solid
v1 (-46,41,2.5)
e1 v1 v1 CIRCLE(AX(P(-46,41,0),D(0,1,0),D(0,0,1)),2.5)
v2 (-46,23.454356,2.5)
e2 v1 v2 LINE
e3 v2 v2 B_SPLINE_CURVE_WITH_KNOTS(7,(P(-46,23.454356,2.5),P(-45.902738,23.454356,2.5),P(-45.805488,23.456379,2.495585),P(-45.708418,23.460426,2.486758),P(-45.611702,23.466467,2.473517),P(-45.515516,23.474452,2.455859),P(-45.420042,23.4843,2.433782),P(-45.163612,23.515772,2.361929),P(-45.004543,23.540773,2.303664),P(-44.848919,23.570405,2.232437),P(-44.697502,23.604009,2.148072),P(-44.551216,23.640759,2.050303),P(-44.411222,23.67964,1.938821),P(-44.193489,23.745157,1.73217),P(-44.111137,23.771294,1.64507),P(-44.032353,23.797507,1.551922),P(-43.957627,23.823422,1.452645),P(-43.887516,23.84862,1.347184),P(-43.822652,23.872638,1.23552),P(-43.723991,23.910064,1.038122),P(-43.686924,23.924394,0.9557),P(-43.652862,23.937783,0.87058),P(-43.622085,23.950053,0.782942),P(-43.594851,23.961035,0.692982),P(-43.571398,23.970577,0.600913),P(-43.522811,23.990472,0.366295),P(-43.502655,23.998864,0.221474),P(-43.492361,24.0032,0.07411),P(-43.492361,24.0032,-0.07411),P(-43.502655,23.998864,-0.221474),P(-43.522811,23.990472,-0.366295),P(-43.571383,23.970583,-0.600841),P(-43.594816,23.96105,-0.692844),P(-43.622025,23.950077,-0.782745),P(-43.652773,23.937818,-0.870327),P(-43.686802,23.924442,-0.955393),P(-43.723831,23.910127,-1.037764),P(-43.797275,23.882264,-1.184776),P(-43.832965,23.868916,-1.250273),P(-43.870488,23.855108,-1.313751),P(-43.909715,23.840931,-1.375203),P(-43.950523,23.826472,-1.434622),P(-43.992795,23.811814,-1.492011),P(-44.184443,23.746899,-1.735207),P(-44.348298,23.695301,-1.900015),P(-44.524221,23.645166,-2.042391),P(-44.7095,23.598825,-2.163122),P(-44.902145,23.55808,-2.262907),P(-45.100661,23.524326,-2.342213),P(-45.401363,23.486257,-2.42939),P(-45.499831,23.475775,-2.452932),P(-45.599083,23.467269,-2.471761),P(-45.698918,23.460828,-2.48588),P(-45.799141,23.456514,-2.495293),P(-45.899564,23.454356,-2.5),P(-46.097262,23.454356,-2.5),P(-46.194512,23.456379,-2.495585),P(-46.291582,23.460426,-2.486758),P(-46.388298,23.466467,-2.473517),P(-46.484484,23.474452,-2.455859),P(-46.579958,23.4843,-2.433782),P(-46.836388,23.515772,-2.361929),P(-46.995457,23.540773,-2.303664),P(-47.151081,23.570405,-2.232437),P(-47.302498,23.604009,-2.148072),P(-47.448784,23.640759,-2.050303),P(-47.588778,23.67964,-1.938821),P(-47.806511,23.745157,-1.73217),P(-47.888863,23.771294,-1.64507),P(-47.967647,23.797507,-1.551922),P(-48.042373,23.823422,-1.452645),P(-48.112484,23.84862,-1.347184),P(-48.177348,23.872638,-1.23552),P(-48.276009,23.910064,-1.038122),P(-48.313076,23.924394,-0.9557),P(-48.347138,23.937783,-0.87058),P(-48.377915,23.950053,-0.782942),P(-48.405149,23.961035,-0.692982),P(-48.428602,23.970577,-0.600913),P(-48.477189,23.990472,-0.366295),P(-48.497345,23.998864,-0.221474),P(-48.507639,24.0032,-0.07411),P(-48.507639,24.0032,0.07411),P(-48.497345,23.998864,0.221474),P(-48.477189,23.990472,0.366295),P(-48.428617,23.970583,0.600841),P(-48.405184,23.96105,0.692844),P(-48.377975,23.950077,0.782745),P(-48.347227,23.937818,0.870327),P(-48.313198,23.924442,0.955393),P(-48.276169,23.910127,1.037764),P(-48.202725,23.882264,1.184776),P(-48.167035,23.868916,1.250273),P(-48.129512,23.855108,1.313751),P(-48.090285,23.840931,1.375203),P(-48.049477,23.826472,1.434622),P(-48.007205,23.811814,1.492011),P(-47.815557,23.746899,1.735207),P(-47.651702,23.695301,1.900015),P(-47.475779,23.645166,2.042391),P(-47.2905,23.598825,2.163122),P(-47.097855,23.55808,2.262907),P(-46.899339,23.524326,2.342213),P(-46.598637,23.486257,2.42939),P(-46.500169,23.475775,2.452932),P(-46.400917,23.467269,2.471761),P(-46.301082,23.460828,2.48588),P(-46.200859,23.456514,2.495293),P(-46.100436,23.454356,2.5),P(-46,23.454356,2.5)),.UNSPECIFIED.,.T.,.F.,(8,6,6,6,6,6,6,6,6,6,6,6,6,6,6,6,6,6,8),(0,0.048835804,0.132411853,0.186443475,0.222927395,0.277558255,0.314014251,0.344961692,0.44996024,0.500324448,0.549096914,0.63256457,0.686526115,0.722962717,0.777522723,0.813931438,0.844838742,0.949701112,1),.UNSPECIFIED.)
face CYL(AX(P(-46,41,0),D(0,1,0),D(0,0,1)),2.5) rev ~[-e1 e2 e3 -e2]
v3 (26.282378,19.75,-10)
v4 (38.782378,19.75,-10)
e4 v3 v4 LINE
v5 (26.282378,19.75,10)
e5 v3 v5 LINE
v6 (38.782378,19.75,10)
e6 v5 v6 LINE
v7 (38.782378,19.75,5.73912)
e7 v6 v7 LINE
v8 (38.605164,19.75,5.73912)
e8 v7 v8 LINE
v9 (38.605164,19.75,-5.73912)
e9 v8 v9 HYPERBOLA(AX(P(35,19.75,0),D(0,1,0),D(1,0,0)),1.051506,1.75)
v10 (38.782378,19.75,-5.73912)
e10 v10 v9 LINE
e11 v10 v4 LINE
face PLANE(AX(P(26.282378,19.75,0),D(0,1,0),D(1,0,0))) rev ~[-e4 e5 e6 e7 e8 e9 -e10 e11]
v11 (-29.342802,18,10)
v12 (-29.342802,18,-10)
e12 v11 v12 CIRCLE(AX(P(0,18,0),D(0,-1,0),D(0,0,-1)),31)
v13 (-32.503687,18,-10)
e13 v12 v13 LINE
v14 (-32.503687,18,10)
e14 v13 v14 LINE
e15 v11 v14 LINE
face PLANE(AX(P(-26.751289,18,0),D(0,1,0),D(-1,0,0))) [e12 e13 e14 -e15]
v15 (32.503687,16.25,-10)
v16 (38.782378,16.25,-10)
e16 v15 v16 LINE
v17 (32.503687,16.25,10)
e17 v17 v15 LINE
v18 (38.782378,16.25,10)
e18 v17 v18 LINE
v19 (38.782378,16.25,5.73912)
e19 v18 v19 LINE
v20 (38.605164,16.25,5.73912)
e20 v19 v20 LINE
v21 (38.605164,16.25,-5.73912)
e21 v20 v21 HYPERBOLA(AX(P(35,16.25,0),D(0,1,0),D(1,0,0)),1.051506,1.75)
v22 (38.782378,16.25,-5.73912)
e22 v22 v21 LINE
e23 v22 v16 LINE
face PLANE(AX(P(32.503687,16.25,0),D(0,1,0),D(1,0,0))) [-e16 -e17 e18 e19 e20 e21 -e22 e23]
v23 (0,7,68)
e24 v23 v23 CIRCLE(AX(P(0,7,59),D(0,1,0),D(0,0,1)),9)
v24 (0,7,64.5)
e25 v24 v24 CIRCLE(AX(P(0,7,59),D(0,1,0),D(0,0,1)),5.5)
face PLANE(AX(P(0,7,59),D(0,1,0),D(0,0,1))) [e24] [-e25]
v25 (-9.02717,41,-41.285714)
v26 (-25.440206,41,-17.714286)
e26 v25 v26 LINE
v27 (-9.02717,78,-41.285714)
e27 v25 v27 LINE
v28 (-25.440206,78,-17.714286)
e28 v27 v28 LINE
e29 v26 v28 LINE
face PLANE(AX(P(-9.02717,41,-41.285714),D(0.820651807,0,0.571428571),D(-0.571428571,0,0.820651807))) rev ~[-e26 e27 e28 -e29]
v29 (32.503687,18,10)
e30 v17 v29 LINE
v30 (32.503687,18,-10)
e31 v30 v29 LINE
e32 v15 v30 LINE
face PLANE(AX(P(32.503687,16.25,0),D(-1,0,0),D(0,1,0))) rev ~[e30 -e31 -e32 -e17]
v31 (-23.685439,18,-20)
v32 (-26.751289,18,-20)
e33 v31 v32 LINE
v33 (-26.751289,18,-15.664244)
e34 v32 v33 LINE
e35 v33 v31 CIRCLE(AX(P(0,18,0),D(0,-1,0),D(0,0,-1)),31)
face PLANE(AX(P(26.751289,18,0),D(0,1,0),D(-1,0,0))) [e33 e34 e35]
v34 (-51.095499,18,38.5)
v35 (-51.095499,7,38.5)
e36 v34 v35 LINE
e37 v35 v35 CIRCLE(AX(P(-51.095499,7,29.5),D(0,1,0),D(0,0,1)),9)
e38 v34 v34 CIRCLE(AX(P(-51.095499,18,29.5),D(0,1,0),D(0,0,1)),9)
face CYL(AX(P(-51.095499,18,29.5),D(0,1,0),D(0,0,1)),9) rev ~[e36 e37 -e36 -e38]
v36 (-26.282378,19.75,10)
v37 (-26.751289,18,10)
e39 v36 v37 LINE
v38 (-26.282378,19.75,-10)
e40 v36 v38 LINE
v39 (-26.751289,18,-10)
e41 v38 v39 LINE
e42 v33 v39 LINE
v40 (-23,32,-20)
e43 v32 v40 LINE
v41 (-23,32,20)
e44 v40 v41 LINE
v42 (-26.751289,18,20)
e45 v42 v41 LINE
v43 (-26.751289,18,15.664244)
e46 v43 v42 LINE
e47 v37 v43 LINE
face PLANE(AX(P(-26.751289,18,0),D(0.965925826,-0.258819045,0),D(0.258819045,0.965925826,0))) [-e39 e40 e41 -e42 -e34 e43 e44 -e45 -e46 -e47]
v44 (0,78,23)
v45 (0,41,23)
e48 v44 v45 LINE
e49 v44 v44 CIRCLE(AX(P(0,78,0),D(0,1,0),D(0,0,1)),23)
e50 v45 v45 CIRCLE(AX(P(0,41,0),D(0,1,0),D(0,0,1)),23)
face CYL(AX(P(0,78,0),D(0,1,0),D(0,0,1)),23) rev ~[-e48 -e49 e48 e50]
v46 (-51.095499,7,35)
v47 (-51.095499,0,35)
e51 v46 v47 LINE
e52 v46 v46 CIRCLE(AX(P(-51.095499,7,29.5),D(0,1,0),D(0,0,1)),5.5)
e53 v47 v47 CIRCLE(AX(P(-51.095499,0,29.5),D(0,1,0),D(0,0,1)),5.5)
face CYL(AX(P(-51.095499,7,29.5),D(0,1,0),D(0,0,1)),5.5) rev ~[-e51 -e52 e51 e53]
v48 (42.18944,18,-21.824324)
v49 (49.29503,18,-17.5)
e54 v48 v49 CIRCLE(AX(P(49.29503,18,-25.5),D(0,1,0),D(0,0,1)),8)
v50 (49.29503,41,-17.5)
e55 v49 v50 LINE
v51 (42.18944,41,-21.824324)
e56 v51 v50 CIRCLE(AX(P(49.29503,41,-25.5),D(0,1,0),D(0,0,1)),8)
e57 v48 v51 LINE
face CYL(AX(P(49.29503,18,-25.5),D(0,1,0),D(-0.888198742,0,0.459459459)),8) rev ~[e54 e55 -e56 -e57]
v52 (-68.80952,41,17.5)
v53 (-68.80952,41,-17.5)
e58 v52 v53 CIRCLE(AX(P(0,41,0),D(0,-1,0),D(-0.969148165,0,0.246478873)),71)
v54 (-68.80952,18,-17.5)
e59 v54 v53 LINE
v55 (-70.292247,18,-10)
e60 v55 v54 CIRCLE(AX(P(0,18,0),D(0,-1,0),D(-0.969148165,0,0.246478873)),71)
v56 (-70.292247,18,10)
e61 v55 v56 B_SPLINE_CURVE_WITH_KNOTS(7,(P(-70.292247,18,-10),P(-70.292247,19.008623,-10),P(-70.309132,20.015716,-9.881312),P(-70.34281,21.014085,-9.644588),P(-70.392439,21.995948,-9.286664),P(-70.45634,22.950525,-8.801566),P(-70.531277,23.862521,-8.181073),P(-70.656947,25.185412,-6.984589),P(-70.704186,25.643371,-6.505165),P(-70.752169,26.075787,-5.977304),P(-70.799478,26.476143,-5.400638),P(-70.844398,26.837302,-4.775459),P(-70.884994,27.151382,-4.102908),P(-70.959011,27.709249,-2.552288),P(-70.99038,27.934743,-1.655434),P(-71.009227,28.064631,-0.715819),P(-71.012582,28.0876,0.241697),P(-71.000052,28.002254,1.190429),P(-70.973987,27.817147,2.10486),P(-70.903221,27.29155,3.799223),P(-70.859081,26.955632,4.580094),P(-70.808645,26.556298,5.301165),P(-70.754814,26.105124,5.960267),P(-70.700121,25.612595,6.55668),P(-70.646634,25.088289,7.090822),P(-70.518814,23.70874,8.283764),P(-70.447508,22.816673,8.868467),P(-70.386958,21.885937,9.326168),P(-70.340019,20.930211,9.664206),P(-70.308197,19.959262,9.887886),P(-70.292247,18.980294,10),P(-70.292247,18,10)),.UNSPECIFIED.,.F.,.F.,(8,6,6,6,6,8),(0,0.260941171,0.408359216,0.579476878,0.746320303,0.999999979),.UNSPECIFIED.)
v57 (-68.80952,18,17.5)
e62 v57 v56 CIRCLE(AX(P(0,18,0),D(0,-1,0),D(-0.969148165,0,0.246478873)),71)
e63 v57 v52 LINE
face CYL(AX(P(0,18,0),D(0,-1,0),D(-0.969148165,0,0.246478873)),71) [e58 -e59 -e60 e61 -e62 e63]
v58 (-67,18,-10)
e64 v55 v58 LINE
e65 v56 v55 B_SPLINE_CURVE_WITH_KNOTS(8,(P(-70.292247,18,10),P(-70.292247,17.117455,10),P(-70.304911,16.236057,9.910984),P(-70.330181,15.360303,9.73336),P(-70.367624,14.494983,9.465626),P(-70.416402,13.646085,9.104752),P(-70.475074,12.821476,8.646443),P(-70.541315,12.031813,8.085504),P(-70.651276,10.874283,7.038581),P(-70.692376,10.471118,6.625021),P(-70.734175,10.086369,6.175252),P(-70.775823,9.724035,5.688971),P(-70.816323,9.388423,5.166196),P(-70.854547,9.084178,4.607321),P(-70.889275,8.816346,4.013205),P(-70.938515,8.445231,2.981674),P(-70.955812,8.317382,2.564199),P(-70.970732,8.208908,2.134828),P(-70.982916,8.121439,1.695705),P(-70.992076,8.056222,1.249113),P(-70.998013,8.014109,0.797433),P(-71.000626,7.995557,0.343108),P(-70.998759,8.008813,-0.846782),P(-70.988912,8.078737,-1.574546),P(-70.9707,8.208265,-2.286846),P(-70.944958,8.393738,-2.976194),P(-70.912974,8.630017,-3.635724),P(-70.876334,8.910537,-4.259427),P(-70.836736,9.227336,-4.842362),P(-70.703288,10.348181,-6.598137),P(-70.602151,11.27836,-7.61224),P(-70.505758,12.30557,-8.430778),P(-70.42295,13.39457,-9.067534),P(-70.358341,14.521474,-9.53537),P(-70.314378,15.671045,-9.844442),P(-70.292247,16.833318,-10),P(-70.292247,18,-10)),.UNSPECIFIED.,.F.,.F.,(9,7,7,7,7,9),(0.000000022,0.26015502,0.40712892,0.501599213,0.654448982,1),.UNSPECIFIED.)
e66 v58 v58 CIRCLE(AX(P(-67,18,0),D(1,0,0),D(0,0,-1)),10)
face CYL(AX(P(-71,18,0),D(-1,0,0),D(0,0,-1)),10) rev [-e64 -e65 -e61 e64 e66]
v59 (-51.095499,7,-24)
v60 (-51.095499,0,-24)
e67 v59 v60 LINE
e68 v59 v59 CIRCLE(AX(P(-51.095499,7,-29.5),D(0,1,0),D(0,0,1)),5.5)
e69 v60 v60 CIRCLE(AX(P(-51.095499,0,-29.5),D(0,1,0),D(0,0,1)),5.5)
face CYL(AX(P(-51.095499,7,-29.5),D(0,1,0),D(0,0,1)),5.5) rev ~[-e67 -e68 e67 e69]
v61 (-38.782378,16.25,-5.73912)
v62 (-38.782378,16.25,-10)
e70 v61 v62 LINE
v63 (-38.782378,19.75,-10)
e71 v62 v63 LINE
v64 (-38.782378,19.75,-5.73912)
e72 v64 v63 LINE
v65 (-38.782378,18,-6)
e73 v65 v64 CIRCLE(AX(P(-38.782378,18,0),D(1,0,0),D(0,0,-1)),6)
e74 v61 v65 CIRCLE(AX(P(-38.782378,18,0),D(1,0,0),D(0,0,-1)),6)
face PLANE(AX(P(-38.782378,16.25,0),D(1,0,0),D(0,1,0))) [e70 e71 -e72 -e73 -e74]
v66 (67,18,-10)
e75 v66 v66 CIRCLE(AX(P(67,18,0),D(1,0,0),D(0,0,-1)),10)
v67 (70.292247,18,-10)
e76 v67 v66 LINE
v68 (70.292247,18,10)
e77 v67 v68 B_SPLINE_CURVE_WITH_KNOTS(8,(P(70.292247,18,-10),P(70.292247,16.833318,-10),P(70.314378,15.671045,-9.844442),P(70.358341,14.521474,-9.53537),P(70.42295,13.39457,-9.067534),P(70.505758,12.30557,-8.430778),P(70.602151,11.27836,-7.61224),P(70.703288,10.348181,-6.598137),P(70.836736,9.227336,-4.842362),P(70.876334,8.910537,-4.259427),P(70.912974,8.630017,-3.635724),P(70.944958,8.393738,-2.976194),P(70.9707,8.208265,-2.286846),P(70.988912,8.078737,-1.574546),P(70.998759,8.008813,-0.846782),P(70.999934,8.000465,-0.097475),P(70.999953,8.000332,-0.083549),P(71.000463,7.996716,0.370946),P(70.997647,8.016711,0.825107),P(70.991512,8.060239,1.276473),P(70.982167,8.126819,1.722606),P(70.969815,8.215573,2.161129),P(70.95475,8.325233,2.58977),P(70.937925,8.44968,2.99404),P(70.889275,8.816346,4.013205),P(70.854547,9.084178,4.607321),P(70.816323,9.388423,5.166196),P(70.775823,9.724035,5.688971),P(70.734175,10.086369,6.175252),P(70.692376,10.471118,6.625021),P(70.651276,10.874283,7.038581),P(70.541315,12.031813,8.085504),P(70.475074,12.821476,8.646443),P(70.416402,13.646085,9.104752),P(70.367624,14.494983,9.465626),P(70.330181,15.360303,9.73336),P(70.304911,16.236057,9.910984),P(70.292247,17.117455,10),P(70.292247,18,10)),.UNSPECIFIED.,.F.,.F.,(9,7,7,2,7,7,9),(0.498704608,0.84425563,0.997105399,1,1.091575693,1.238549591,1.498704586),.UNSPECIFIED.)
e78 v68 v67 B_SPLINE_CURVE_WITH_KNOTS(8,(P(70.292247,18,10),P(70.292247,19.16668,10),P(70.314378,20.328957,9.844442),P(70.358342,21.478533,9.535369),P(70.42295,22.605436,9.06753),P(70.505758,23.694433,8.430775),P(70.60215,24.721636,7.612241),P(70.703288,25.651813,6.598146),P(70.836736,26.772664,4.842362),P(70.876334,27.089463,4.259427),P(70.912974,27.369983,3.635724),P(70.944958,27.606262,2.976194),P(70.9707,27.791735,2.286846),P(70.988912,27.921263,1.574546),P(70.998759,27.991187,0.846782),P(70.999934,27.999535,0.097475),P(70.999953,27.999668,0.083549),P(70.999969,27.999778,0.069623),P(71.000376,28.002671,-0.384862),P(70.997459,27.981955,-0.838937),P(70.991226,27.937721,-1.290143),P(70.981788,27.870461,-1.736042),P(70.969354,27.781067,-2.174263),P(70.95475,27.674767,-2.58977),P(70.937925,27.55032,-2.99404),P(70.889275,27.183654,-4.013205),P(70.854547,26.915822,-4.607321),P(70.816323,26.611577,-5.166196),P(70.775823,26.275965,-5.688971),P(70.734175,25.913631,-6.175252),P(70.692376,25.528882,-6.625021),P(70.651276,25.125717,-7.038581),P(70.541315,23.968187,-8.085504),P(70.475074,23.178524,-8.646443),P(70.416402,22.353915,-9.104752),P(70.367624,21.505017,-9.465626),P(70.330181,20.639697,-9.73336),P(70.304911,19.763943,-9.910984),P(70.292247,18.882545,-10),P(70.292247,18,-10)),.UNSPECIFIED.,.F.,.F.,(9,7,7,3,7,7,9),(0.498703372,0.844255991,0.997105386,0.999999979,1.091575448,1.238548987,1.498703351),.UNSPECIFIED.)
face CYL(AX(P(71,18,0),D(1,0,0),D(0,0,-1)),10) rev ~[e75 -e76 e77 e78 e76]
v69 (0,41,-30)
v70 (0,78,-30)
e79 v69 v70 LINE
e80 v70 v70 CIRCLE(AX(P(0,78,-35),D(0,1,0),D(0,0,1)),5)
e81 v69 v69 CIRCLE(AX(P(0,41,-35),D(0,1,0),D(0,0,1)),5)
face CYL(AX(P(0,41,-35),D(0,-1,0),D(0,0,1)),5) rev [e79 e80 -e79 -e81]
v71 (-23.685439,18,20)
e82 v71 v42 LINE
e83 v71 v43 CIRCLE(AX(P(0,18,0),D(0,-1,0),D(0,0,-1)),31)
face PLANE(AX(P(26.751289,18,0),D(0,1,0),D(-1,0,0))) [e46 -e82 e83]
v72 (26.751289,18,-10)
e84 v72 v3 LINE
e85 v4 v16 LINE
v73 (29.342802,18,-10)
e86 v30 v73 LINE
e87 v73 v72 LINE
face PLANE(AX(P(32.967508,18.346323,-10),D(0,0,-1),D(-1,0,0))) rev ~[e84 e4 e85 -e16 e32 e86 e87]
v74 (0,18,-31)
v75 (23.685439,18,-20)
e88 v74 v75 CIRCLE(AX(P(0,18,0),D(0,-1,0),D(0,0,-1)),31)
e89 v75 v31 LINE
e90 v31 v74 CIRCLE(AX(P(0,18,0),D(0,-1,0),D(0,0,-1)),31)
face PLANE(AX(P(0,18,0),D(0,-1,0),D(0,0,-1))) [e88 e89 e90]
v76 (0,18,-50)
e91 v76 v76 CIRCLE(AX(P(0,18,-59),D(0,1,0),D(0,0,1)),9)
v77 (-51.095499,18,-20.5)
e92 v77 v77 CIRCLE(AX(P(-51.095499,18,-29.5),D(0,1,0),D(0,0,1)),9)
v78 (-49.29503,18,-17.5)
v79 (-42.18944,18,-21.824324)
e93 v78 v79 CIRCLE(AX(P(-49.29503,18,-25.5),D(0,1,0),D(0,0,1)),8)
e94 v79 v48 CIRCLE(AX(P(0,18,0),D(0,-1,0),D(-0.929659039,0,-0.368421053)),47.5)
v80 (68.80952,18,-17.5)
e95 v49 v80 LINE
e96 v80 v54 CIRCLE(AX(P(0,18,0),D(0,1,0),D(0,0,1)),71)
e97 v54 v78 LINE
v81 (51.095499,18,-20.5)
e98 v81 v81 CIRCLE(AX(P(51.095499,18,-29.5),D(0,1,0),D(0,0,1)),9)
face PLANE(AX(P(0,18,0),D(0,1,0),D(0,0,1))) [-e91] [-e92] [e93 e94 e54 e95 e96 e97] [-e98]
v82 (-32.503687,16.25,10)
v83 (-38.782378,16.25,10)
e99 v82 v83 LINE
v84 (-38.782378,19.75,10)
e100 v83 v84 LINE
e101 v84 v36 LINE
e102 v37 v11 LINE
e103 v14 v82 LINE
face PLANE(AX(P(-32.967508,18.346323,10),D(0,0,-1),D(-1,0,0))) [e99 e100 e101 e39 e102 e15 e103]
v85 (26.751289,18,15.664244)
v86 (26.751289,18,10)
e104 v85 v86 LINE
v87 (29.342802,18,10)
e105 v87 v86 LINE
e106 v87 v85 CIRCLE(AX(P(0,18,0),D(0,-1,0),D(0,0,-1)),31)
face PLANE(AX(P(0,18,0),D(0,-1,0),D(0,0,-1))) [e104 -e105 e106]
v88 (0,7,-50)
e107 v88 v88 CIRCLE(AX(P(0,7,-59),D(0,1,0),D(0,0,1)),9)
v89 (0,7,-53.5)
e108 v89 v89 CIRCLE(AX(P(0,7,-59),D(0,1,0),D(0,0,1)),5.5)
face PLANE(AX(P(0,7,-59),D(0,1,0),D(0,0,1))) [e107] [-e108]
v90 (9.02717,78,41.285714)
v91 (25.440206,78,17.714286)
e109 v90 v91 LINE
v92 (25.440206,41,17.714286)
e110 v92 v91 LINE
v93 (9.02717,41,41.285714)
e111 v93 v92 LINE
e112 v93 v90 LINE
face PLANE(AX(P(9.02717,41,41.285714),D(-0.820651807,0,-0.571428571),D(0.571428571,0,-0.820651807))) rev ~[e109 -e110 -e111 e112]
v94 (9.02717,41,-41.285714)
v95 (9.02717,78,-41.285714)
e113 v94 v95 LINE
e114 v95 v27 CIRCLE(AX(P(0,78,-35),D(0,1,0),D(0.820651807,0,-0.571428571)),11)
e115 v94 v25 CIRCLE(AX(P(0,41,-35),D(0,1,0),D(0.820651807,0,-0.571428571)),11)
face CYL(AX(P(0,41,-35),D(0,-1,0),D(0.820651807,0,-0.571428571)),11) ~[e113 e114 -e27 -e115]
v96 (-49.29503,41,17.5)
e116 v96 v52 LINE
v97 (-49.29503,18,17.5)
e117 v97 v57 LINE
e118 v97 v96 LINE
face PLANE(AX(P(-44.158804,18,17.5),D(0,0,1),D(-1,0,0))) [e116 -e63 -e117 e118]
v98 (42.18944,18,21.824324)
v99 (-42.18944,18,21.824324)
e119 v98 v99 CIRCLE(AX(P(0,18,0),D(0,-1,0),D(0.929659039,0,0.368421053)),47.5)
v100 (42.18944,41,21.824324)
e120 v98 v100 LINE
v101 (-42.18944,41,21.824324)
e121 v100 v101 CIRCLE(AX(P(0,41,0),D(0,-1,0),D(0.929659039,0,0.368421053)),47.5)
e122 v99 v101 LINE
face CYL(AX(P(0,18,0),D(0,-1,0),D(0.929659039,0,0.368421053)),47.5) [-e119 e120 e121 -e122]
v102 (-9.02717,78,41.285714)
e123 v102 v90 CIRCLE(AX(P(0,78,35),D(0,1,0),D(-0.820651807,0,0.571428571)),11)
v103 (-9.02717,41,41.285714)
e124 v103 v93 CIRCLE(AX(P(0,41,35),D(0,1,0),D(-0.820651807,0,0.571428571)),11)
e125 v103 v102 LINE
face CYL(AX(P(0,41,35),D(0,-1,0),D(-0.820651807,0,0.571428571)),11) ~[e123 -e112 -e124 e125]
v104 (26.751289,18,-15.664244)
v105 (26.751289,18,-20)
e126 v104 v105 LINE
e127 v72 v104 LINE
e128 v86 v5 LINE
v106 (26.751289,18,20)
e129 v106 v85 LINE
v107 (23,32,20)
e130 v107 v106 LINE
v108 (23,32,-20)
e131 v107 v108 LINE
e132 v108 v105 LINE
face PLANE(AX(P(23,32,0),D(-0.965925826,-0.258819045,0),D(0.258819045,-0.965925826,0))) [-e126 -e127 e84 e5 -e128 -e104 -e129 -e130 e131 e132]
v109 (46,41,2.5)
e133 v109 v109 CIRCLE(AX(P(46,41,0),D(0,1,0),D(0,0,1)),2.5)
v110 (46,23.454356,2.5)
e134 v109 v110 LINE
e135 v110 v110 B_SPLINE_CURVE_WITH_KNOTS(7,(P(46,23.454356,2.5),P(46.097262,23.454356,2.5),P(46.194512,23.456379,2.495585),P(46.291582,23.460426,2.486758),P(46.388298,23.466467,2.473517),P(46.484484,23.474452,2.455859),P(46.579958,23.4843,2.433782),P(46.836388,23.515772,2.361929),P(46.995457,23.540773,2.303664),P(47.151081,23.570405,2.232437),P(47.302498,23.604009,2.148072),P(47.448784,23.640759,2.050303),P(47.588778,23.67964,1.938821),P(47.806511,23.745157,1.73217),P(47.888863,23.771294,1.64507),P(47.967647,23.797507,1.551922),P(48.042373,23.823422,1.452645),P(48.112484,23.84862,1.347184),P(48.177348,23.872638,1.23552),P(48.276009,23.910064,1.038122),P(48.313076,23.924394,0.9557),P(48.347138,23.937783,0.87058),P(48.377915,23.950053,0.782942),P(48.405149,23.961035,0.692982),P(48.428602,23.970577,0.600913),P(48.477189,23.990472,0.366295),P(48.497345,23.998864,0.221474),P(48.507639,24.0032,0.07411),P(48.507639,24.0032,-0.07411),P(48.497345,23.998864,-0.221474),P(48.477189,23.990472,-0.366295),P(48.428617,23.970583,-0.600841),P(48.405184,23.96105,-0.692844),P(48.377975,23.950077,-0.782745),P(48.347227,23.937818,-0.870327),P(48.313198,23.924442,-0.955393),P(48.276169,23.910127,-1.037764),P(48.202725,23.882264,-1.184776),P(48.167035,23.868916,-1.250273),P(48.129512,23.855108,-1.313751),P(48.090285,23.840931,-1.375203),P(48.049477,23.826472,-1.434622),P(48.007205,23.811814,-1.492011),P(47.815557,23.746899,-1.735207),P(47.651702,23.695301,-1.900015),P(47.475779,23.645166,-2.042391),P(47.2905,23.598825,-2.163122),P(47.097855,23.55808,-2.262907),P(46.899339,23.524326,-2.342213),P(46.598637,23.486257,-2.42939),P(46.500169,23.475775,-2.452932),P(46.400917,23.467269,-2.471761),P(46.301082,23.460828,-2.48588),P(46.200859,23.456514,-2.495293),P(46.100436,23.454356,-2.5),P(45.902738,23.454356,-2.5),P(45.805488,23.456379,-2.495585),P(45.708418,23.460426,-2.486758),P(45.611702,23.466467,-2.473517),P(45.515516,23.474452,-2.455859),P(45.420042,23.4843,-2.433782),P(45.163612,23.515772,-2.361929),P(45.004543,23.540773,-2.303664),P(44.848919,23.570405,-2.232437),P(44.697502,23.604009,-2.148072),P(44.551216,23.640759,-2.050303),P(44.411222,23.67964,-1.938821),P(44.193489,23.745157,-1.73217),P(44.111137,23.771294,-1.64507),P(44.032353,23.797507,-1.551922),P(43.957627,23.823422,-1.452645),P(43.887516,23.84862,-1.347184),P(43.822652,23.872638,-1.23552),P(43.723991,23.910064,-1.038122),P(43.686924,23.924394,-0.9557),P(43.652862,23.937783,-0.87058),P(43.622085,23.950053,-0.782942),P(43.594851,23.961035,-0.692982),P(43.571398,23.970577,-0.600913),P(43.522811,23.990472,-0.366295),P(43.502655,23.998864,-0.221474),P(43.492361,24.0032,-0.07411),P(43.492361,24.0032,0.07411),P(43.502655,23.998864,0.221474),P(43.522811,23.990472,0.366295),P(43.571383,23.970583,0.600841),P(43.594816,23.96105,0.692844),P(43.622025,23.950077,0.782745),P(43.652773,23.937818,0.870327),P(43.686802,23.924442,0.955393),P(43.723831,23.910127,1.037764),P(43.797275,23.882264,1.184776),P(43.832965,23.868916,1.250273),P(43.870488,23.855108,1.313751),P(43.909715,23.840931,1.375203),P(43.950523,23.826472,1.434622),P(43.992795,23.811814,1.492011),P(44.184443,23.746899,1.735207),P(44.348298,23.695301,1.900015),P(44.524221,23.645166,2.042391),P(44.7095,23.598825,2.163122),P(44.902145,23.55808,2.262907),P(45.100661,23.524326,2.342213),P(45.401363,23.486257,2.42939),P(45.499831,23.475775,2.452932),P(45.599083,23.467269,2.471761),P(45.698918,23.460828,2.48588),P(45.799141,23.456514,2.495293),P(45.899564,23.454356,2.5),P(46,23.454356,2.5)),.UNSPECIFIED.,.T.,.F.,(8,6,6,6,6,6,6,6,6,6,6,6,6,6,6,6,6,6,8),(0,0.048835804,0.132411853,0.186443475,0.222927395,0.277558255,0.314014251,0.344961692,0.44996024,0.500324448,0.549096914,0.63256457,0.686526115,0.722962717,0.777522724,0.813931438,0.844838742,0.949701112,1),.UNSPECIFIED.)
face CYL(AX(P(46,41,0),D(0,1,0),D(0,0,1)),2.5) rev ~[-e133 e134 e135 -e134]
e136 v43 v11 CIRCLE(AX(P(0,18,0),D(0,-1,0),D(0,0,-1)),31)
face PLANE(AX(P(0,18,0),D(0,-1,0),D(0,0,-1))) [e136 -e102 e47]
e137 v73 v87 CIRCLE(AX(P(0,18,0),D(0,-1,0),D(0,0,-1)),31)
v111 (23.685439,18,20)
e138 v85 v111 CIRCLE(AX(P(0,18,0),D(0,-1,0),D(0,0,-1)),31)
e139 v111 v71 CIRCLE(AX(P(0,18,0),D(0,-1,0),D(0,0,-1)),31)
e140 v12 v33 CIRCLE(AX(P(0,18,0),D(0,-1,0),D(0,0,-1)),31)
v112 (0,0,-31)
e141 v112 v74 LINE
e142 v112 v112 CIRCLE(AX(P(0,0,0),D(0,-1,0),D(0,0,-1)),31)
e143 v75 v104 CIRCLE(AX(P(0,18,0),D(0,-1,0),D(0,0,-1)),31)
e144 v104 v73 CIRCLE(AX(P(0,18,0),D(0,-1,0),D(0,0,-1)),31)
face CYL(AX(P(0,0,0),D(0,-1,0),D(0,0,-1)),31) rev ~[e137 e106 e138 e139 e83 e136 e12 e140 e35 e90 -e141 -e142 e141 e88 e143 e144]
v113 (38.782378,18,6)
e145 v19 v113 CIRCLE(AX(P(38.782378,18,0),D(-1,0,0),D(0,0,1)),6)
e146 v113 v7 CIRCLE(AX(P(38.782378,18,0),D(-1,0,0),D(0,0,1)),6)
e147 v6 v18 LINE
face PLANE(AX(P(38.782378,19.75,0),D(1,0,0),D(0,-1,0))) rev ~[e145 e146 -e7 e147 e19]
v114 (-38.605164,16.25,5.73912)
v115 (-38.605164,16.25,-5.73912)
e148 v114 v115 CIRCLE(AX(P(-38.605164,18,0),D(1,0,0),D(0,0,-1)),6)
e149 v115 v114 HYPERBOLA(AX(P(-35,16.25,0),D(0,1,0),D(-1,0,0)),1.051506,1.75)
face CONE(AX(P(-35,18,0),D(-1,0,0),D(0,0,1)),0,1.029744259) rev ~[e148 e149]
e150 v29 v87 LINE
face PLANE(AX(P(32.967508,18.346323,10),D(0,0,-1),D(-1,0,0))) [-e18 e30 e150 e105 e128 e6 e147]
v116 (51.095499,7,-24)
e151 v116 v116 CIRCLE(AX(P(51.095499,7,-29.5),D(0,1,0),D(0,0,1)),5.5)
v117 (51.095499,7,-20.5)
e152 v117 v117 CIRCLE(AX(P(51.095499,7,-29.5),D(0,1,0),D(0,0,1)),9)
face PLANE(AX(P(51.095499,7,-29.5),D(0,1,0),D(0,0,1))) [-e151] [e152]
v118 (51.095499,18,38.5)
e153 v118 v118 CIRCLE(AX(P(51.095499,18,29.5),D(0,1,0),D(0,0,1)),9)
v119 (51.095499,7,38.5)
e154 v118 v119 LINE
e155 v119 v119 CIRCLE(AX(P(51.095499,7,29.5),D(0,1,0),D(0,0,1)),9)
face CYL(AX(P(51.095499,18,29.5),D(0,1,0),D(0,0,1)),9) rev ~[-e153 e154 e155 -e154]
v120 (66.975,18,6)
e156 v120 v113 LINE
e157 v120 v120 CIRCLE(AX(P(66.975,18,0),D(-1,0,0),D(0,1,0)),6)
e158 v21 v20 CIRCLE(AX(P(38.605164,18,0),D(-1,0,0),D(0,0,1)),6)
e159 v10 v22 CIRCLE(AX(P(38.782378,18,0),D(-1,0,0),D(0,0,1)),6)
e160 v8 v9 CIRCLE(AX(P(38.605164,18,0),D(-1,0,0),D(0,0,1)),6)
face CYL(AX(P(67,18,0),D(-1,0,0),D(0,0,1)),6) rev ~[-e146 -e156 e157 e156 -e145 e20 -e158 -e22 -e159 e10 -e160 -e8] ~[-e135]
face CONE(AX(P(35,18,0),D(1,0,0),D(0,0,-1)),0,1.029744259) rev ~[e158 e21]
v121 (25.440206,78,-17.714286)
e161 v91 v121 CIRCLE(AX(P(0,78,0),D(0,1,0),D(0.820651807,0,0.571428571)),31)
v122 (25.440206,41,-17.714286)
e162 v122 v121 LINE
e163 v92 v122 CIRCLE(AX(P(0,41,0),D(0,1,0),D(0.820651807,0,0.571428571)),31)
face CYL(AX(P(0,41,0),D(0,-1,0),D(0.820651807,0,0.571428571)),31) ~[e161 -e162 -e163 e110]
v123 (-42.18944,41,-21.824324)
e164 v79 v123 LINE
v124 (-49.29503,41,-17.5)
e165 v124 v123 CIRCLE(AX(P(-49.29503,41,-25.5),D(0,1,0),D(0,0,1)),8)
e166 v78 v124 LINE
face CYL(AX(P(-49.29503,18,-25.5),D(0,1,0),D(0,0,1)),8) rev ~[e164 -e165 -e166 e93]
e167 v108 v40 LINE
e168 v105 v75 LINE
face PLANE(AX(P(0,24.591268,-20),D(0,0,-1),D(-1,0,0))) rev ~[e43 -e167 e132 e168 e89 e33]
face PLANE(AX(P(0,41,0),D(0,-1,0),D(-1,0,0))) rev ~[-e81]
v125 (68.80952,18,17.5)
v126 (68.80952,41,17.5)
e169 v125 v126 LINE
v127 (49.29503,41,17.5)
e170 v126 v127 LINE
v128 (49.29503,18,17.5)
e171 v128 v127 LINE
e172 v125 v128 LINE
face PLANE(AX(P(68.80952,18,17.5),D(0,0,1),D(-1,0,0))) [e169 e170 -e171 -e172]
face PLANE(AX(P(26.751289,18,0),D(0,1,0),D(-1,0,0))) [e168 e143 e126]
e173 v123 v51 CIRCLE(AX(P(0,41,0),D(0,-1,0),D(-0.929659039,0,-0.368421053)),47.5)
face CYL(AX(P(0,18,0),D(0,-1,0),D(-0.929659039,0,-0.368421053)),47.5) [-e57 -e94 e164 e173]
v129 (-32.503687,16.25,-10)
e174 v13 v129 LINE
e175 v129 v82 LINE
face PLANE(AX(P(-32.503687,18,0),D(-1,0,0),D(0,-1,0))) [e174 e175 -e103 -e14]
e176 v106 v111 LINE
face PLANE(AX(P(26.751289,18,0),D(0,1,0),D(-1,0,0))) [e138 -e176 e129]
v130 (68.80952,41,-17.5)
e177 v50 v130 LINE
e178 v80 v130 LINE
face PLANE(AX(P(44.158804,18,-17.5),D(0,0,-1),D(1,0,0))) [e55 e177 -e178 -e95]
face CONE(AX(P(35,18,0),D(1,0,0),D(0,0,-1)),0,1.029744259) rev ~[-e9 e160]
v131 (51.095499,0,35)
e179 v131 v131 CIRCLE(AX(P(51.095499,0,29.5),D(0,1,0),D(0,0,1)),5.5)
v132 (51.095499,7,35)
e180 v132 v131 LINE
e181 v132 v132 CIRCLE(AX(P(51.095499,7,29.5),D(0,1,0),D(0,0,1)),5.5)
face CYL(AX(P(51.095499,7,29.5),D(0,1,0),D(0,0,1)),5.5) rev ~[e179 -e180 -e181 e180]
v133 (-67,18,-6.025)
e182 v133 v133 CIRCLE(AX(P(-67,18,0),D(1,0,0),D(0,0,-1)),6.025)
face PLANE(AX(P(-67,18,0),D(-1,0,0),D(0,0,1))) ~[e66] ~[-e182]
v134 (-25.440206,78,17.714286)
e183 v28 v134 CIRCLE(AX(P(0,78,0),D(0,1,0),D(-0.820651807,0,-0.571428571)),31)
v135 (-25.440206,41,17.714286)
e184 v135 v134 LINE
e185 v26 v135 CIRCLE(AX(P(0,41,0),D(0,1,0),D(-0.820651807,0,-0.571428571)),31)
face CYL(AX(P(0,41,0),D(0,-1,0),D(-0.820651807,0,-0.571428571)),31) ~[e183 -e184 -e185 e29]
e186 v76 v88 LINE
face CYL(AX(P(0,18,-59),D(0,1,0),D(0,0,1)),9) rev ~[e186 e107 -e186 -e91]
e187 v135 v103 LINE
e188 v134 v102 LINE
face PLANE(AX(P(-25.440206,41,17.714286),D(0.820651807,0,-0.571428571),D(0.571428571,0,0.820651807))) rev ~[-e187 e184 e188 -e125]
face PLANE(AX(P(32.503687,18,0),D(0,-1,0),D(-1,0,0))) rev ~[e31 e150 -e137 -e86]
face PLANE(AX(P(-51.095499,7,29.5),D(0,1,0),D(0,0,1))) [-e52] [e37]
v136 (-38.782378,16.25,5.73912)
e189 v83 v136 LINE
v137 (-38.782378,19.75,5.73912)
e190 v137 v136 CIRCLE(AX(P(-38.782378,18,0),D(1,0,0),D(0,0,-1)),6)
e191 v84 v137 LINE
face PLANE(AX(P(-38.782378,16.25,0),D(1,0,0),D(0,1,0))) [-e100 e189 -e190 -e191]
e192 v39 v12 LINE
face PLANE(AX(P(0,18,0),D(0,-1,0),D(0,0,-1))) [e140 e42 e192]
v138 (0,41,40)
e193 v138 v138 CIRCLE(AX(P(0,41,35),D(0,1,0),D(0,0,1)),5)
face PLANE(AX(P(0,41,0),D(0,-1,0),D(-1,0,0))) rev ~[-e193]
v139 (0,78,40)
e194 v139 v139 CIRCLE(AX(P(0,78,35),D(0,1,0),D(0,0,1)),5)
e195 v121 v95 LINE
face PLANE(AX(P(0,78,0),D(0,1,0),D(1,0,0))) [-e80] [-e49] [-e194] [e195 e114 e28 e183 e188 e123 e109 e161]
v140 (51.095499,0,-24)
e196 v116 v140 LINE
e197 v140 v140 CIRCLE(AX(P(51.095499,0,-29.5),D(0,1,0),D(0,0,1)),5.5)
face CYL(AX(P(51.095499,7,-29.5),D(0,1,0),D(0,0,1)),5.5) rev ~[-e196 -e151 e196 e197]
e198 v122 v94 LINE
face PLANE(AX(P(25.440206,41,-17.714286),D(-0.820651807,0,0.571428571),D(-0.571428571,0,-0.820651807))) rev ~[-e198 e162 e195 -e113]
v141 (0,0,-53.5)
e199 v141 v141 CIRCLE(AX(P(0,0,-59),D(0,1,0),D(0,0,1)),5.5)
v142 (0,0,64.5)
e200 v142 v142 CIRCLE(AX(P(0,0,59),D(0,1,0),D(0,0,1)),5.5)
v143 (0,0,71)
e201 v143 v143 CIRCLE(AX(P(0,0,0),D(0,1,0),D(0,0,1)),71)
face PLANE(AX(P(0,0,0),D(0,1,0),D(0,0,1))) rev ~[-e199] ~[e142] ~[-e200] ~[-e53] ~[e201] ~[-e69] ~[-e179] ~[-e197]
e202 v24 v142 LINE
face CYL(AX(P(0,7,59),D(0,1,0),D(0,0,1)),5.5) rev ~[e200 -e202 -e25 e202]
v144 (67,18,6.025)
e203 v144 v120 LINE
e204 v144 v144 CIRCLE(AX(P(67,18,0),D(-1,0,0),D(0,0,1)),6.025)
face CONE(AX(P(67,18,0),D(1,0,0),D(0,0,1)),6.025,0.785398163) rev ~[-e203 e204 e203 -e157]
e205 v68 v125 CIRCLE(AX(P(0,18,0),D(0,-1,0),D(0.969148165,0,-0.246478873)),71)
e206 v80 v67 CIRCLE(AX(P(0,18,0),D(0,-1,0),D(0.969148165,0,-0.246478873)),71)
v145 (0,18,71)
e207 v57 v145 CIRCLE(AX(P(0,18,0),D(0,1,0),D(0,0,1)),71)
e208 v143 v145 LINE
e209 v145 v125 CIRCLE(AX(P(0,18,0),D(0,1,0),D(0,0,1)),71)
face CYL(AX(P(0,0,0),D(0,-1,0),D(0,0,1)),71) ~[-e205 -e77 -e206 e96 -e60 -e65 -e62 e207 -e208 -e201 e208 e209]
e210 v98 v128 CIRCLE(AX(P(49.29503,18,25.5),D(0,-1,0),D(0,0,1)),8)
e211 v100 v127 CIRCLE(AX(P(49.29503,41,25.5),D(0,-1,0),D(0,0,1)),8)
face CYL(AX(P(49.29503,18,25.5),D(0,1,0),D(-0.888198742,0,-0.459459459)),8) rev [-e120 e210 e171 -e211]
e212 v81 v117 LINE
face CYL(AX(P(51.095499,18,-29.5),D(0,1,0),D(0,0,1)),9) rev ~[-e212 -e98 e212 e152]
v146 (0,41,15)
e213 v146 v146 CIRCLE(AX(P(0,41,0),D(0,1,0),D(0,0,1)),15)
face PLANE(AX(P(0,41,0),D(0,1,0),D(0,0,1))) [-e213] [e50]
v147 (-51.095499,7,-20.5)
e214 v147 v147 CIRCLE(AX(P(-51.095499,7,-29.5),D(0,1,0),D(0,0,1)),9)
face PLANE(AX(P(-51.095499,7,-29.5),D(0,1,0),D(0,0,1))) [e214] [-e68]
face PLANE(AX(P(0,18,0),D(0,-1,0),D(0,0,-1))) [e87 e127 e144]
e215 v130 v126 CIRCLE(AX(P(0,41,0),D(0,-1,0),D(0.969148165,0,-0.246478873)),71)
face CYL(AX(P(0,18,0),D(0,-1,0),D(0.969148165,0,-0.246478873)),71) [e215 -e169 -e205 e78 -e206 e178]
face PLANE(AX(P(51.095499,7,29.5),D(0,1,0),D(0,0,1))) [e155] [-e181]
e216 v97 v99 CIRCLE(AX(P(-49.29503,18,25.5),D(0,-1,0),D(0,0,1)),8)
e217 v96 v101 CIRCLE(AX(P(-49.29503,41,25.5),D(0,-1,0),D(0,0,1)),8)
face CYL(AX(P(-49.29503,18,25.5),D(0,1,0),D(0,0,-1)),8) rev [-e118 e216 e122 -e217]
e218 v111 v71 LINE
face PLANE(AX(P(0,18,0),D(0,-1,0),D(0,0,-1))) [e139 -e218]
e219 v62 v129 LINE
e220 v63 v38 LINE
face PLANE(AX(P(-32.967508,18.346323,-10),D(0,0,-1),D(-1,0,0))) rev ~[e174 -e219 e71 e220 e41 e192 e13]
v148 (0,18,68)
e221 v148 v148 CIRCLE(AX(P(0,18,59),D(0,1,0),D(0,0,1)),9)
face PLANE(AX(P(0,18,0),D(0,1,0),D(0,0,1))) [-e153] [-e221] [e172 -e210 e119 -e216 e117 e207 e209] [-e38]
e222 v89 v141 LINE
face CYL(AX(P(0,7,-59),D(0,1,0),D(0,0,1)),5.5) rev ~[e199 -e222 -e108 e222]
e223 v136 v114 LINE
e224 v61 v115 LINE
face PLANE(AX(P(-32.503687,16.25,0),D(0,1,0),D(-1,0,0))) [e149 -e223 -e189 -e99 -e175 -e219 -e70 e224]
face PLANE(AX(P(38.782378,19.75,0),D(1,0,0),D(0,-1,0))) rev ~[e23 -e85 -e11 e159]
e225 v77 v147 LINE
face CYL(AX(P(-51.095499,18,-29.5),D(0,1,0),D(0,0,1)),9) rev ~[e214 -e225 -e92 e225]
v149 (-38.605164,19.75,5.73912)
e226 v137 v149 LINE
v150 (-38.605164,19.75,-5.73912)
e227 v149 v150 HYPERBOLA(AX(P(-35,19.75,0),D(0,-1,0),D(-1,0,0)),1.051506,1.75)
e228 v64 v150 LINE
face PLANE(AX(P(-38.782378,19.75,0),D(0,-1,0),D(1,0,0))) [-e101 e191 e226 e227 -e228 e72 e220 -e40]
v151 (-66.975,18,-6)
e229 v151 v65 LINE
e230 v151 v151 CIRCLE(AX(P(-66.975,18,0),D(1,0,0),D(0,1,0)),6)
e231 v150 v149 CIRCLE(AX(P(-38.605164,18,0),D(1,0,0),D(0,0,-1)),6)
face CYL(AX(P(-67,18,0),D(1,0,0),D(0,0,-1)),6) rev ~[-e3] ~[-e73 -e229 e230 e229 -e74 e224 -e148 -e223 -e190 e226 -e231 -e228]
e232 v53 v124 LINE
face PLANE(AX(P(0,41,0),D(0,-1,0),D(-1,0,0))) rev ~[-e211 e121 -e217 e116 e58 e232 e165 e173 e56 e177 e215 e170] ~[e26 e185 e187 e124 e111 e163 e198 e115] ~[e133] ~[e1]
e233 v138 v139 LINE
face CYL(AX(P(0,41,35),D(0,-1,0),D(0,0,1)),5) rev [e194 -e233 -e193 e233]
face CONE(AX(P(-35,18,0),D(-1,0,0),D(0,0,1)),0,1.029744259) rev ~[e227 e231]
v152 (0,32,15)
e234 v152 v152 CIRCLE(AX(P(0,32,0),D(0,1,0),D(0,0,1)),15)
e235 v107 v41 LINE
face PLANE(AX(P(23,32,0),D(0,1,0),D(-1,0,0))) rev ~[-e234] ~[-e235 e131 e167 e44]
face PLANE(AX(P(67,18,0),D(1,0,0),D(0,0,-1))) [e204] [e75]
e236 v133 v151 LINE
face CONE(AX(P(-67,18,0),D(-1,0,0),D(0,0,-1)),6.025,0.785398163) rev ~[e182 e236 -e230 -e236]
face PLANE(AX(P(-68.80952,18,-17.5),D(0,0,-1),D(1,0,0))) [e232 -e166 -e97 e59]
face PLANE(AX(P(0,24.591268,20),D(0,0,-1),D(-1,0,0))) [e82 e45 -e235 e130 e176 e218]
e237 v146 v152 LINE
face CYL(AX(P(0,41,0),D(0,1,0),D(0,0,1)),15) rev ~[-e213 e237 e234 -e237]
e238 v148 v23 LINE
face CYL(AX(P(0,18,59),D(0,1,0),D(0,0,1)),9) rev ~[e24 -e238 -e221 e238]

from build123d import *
from build123d.topology import SkipClean

# Parameters (mm, degrees)
BASE_FLANGE_SKETCH_R             = 71
BASE_FLANGE_142_DEPTH            = 18
COUNTERBORE_SKETCH_R             = 9
BOLT_COUNTERBORES_6X_18_DEPTH    = 11
BOLT_HOLE_SKETCH_R               = 5.5
BOLT_HOLES_6X_11_DEPTH           = 11
RAISED_BODY_DEPTH                = 23
SIDE_SPOT_FACE_SKETCH_R          = 10
SIDE_SPOT_FACE_20_DEPTH          = 4
BEARING_RECESS_SKETCH_R          = 31
BEARING_RECESS_62_DEPTH          = 18
BORE_30_SKETCH_R                 = 15
BORE_30_DEPTH                    = 9
ANGLED_CLEARANCE_CUT_DEPTH       = 20
TOP_FLANGE_BOSS_SKETCH_R         = 5
TOP_FLANGE_BOSS_DEPTH            = 37
TOP_BORE_SKETCH_R                = 23
TOP_BORE_46_DEPTH                = 37
TOP_FLANGE_HOLES_SKETCH_R        = 2.5
TOP_FLANGE_HOLES_2X_5_DEPTH      = 25
SIDE_DOWEL_HOLE_12_A_D           = 12
SIDE_DOWEL_HOLE_12_A_DEPTH       = 28.394836286
SIDE_DOWEL_HOLE_12_A_CSINK_D     = 12.05
SIDE_DOWEL_HOLE_12_A_CSINK_ANGLE = 90
SIDE_DOWEL_HOLE_12_A_TIP         = 3.605163714
SIDE_DOWEL_HOLE_12_B_D           = 12
SIDE_DOWEL_HOLE_12_B_DEPTH       = 28.394836286
SIDE_DOWEL_HOLE_12_B_CSINK_D     = 12.05
SIDE_DOWEL_HOLE_12_B_CSINK_ANGLE = 90
SIDE_DOWEL_HOLE_12_B_TIP         = 3.605163714
SIDE_PORT_CUT_DEPTH              = 10
BODY_FILLETS_R8_R                = 8


with BuildPart() as part:
    # Base Flange Sketch → Base Flange Ø142 (new body)
    with BuildSketch(Plane(origin=(0, 0, 0), x_dir=(1, 0, 0), z_dir=(0, 1, 0))):
        with Locations(Location((0, 0, 0), (0, 0, 270))):
            Circle(BASE_FLANGE_SKETCH_R)
    extrude(amount=BASE_FLANGE_142_DEPTH)

    # Counterbore Sketch → Bolt Counterbores 6xØ18 (cut)
    with BuildSketch(Plane(origin=(0, 18, 0), x_dir=(1, 0, 0), z_dir=(0, 1, 0))):
        with Locations(Location((0, 59, 0), (0, 0, 270))):
            Circle(COUNTERBORE_SKETCH_R)
        with Locations(Location((51.095498823, 29.5, 0), (0, 0, 270))):
            Circle(COUNTERBORE_SKETCH_R)
        with Locations(Location((51.095498823, -29.5, 0), (0, 0, 270))):
            Circle(COUNTERBORE_SKETCH_R)
        with Locations(Location((0, -59, 0), (0, 0, 270))):
            Circle(COUNTERBORE_SKETCH_R)
        with Locations(Location((-51.095498823, -29.5, 0), (0, 0, 270))):
            Circle(COUNTERBORE_SKETCH_R)
        with Locations(Location((-51.095498823, 29.5, 0), (0, 0, 270))):
            Circle(COUNTERBORE_SKETCH_R)
    extrude(amount=-BOLT_COUNTERBORES_6X_18_DEPTH, mode=Mode.SUBTRACT)

    # Bolt Hole Sketch → Bolt Holes 6xØ11 (cut)
    with BuildSketch(Plane(origin=(0, 7, 0), x_dir=(1, 0, 0), z_dir=(0, 1, 0))):
        with Locations(Location((-51.095498823, 29.5, 0), (0, 0, 270))):
            Circle(BOLT_HOLE_SKETCH_R)
        with Locations(Location((0, 59, 0), (0, 0, 270))):
            Circle(BOLT_HOLE_SKETCH_R)
        with Locations(Location((51.095498823, 29.5, 0), (0, 0, 270))):
            Circle(BOLT_HOLE_SKETCH_R)
        with Locations(Location((51.095498823, -29.5, 0), (0, 0, 270))):
            Circle(BOLT_HOLE_SKETCH_R)
        with Locations(Location((0, -59, 0), (0, 0, 270))):
            Circle(BOLT_HOLE_SKETCH_R)
        with Locations(Location((-51.095498823, -29.5, 0), (0, 0, 270))):
            Circle(BOLT_HOLE_SKETCH_R)
    extrude(amount=-BOLT_HOLES_6X_11_DEPTH, mode=Mode.SUBTRACT)

    # Raised Body Sketch → Raised Body (add)
    with SkipClean():  # the faces are left unmerged after this step: merging them gives an invalid solid
        with BuildSketch(Plane(origin=(0, 18, 0), x_dir=(1, 0, 0), z_dir=(0, 1, 0))):
            with BuildLine():
                Line((-68.80951969, 17.5), (-44.158804332, 17.5))
                ThreePointArc((-44.158804332, 17.5), (0, 47.5), (44.158804332, 17.5))
                Line((44.158804332, 17.5), (68.80951969, 17.5))
                ThreePointArc((68.80951969, 17.5), (71, 0), (68.80951969, -17.5))
                Line((68.80951969, -17.5), (44.158804332, -17.5))
                ThreePointArc((44.158804332, -17.5), (0, -47.5), (-44.158804332, -17.5))
                Line((-44.158804332, -17.5), (-68.80951969, -17.5))
                ThreePointArc((-68.80951969, -17.5), (-71, 0), (-68.80951969, 17.5))
            make_face()
        extrude(amount=RAISED_BODY_DEPTH)

    # Side Spot Face Sketch → Side Spot Face Ø20 (cut)
    with BuildSketch(Plane(origin=(71, 0, 0), x_dir=(0, 0, -1), z_dir=(1, 0, 0))):
        with Locations((0, 18)):
            Circle(SIDE_SPOT_FACE_SKETCH_R)
    side_spot_face_20 = extrude(amount=-SIDE_SPOT_FACE_20_DEPTH, mode=Mode.SUBTRACT)

    # Side Spot Face Mirror: Side Spot Face Ø20 across plane
    add(side_spot_face_20.mirror(Plane(origin=(0, 0, 0), x_dir=(0, 0, 1), z_dir=(1, 0, 0))), mode=Mode.SUBTRACT)

    # Bearing Recess Sketch → Bearing Recess Ø62 (cut)
    with SkipClean():  # the faces are left unmerged after this step: merging them gives an invalid solid
        with BuildSketch(Plane.XZ):
            with Locations(Location((0, 0, 0), (0, 0, 270))):
                Circle(BEARING_RECESS_SKETCH_R)
        extrude(amount=-BEARING_RECESS_62_DEPTH, mode=Mode.SUBTRACT)

    # Bore Ø30 Sketch → Bore Ø30 (cut)
    with SkipClean():  # the faces are left unmerged after this step: merging them gives an invalid solid
        with BuildSketch(Plane(origin=(0, 41, 0), x_dir=(1, 0, 0), z_dir=(0, 1, 0))):
            with Locations(Location((0, 0, 0), (0, 0, 270))):
                Circle(BORE_30_SKETCH_R)
        extrude(amount=-BORE_30_DEPTH, mode=Mode.SUBTRACT)

    # Angled Cut Sketch → Angled Clearance Cut (cut, symmetric)
    with SkipClean():  # the faces are left unmerged after this step: merging them gives an invalid solid
        with BuildSketch(Plane.XY):
            Polygon((0, 32), (23, 32), (26.751288694, 18), (-26.751288694, 18), (-23, 32), align=None)
        extrude(amount=ANGLED_CLEARANCE_CUT_DEPTH, both=True, mode=Mode.SUBTRACT)

    # Top Flange Boss Sketch → Top Flange Boss (add)
    with SkipClean():  # the faces are left unmerged after this step: merging them gives an invalid solid
        with BuildSketch(Plane(origin=(0, 41, 0), x_dir=(1, 0, 0), z_dir=(0, 1, 0))):
            with BuildLine():
                Line((-9.027169873, 41.285714286), (-25.440206006, 17.714285714))
                ThreePointArc((-25.440206006, 17.714285714), (-31, 0), (-25.440206006, -17.714285714))
                Line((-25.440206006, -17.714285714), (-9.027169873, -41.285714286))
                ThreePointArc((-9.027169873, -41.285714286), (0, -46), (9.027169873, -41.285714286))
                Line((9.027169873, -41.285714286), (25.440206006, -17.714285714))
                ThreePointArc((25.440206006, -17.714285714), (31, 0), (25.440206006, 17.714285714))
                Line((25.440206006, 17.714285714), (9.027169873, 41.285714286))
                ThreePointArc((9.027169873, 41.285714286), (0, 46), (-9.027169873, 41.285714286))
            make_face()
            with Locations(Location((0, 35, 0), (0, 0, 270))):
                Circle(TOP_FLANGE_BOSS_SKETCH_R, mode=Mode.SUBTRACT)
            with Locations(Location((0, -35, 0), (0, 0, 270))):
                Circle(TOP_FLANGE_BOSS_SKETCH_R, mode=Mode.SUBTRACT)
        extrude(amount=TOP_FLANGE_BOSS_DEPTH)

    # Top Bore Sketch → Top Bore Ø46 (cut)
    with SkipClean():  # the faces are left unmerged after this step: merging them gives an invalid solid
        with BuildSketch(Plane(origin=(0, 78, 0), x_dir=(1, 0, 0), z_dir=(0, 1, 0))):
            with Locations(Location((0, 0, 0), (0, 0, 270))):
                Circle(TOP_BORE_SKETCH_R)
        extrude(amount=-TOP_BORE_46_DEPTH, mode=Mode.SUBTRACT)

    # Top Flange Holes Sketch → Top Flange Holes 2xØ5 (cut)
    with SkipClean():  # the faces are left unmerged after this step: merging them gives an invalid solid
        with BuildSketch(Plane(origin=(0, 41, 0), x_dir=(1, 0, 0), z_dir=(0, 1, 0))):
            with Locations(Location((-46, 0, 0), (0, 0, 270))):
                Circle(TOP_FLANGE_HOLES_SKETCH_R)
            with Locations(Location((46, 0, 0), (0, 0, 270))):
                Circle(TOP_FLANGE_HOLES_SKETCH_R)
        extrude(amount=-TOP_FLANGE_HOLES_2X_5_DEPTH, mode=Mode.SUBTRACT)

    # Side Dowel Hole Ø12 A
    with Locations(Plane(origin=(67, 0, 0), x_dir=(0, 0, -1), z_dir=(1, 0, 0))):
        with Locations((0, 18)):
            CounterSinkHole(SIDE_DOWEL_HOLE_12_A_D / 2, SIDE_DOWEL_HOLE_12_A_CSINK_D / 2, depth=SIDE_DOWEL_HOLE_12_A_DEPTH, counter_sink_angle=SIDE_DOWEL_HOLE_12_A_CSINK_ANGLE)
            with Locations((0, 0, -(SIDE_DOWEL_HOLE_12_A_DEPTH + SIDE_DOWEL_HOLE_12_A_TIP / 2))):  # 118° drill point
                Cone(0, SIDE_DOWEL_HOLE_12_A_D / 2, SIDE_DOWEL_HOLE_12_A_TIP, mode=Mode.SUBTRACT)

    # Side Dowel Hole Ø12 B
    with Locations(Plane.ZY.offset(67)):
        with Locations((0, 18)):
            CounterSinkHole(SIDE_DOWEL_HOLE_12_B_D / 2, SIDE_DOWEL_HOLE_12_B_CSINK_D / 2, depth=SIDE_DOWEL_HOLE_12_B_DEPTH, counter_sink_angle=SIDE_DOWEL_HOLE_12_B_CSINK_ANGLE)
            with Locations((0, 0, -(SIDE_DOWEL_HOLE_12_B_DEPTH + SIDE_DOWEL_HOLE_12_B_TIP / 2))):  # 118° drill point
                Cone(0, SIDE_DOWEL_HOLE_12_B_D / 2, SIDE_DOWEL_HOLE_12_B_TIP, mode=Mode.SUBTRACT)

    # Side Port Sketch → Side Port Cut (cut, symmetric)
    with SkipClean():  # the faces are left unmerged after this step: merging them gives an invalid solid
        with BuildSketch(Plane.XY):
            Polygon((26.282377607, 19.75), (38.782377607, 19.75), (38.782377607, 16.25), (32.580792191, 16.25), (32.503686566, 16.25), (32.503686566, 18), (26.751288694, 18), align=None)
            Polygon((-32.503686566, 16.25), (-32.580792191, 16.25), (-38.782377607, 16.25), (-38.782377607, 19.75), (-26.282377607, 19.75), (-26.751288694, 18), (-32.503686566, 18), align=None)
        extrude(amount=SIDE_PORT_CUT_DEPTH, both=True, mode=Mode.SUBTRACT)

    # Body Fillets R8
    body_fillets_r8_edges = [part.edges().sort_by_distance(p)[0] for p in [
        (-44.158804332, 29.5, 17.5),
        (44.158804332, 29.5, 17.5),
        (44.158804332, 29.5, -17.5),
        (-44.158804332, 29.5, -17.5),
    ]]
    fillet(body_fillets_r8_edges, radius=BODY_FILLETS_R8_R)


solid = part.part
